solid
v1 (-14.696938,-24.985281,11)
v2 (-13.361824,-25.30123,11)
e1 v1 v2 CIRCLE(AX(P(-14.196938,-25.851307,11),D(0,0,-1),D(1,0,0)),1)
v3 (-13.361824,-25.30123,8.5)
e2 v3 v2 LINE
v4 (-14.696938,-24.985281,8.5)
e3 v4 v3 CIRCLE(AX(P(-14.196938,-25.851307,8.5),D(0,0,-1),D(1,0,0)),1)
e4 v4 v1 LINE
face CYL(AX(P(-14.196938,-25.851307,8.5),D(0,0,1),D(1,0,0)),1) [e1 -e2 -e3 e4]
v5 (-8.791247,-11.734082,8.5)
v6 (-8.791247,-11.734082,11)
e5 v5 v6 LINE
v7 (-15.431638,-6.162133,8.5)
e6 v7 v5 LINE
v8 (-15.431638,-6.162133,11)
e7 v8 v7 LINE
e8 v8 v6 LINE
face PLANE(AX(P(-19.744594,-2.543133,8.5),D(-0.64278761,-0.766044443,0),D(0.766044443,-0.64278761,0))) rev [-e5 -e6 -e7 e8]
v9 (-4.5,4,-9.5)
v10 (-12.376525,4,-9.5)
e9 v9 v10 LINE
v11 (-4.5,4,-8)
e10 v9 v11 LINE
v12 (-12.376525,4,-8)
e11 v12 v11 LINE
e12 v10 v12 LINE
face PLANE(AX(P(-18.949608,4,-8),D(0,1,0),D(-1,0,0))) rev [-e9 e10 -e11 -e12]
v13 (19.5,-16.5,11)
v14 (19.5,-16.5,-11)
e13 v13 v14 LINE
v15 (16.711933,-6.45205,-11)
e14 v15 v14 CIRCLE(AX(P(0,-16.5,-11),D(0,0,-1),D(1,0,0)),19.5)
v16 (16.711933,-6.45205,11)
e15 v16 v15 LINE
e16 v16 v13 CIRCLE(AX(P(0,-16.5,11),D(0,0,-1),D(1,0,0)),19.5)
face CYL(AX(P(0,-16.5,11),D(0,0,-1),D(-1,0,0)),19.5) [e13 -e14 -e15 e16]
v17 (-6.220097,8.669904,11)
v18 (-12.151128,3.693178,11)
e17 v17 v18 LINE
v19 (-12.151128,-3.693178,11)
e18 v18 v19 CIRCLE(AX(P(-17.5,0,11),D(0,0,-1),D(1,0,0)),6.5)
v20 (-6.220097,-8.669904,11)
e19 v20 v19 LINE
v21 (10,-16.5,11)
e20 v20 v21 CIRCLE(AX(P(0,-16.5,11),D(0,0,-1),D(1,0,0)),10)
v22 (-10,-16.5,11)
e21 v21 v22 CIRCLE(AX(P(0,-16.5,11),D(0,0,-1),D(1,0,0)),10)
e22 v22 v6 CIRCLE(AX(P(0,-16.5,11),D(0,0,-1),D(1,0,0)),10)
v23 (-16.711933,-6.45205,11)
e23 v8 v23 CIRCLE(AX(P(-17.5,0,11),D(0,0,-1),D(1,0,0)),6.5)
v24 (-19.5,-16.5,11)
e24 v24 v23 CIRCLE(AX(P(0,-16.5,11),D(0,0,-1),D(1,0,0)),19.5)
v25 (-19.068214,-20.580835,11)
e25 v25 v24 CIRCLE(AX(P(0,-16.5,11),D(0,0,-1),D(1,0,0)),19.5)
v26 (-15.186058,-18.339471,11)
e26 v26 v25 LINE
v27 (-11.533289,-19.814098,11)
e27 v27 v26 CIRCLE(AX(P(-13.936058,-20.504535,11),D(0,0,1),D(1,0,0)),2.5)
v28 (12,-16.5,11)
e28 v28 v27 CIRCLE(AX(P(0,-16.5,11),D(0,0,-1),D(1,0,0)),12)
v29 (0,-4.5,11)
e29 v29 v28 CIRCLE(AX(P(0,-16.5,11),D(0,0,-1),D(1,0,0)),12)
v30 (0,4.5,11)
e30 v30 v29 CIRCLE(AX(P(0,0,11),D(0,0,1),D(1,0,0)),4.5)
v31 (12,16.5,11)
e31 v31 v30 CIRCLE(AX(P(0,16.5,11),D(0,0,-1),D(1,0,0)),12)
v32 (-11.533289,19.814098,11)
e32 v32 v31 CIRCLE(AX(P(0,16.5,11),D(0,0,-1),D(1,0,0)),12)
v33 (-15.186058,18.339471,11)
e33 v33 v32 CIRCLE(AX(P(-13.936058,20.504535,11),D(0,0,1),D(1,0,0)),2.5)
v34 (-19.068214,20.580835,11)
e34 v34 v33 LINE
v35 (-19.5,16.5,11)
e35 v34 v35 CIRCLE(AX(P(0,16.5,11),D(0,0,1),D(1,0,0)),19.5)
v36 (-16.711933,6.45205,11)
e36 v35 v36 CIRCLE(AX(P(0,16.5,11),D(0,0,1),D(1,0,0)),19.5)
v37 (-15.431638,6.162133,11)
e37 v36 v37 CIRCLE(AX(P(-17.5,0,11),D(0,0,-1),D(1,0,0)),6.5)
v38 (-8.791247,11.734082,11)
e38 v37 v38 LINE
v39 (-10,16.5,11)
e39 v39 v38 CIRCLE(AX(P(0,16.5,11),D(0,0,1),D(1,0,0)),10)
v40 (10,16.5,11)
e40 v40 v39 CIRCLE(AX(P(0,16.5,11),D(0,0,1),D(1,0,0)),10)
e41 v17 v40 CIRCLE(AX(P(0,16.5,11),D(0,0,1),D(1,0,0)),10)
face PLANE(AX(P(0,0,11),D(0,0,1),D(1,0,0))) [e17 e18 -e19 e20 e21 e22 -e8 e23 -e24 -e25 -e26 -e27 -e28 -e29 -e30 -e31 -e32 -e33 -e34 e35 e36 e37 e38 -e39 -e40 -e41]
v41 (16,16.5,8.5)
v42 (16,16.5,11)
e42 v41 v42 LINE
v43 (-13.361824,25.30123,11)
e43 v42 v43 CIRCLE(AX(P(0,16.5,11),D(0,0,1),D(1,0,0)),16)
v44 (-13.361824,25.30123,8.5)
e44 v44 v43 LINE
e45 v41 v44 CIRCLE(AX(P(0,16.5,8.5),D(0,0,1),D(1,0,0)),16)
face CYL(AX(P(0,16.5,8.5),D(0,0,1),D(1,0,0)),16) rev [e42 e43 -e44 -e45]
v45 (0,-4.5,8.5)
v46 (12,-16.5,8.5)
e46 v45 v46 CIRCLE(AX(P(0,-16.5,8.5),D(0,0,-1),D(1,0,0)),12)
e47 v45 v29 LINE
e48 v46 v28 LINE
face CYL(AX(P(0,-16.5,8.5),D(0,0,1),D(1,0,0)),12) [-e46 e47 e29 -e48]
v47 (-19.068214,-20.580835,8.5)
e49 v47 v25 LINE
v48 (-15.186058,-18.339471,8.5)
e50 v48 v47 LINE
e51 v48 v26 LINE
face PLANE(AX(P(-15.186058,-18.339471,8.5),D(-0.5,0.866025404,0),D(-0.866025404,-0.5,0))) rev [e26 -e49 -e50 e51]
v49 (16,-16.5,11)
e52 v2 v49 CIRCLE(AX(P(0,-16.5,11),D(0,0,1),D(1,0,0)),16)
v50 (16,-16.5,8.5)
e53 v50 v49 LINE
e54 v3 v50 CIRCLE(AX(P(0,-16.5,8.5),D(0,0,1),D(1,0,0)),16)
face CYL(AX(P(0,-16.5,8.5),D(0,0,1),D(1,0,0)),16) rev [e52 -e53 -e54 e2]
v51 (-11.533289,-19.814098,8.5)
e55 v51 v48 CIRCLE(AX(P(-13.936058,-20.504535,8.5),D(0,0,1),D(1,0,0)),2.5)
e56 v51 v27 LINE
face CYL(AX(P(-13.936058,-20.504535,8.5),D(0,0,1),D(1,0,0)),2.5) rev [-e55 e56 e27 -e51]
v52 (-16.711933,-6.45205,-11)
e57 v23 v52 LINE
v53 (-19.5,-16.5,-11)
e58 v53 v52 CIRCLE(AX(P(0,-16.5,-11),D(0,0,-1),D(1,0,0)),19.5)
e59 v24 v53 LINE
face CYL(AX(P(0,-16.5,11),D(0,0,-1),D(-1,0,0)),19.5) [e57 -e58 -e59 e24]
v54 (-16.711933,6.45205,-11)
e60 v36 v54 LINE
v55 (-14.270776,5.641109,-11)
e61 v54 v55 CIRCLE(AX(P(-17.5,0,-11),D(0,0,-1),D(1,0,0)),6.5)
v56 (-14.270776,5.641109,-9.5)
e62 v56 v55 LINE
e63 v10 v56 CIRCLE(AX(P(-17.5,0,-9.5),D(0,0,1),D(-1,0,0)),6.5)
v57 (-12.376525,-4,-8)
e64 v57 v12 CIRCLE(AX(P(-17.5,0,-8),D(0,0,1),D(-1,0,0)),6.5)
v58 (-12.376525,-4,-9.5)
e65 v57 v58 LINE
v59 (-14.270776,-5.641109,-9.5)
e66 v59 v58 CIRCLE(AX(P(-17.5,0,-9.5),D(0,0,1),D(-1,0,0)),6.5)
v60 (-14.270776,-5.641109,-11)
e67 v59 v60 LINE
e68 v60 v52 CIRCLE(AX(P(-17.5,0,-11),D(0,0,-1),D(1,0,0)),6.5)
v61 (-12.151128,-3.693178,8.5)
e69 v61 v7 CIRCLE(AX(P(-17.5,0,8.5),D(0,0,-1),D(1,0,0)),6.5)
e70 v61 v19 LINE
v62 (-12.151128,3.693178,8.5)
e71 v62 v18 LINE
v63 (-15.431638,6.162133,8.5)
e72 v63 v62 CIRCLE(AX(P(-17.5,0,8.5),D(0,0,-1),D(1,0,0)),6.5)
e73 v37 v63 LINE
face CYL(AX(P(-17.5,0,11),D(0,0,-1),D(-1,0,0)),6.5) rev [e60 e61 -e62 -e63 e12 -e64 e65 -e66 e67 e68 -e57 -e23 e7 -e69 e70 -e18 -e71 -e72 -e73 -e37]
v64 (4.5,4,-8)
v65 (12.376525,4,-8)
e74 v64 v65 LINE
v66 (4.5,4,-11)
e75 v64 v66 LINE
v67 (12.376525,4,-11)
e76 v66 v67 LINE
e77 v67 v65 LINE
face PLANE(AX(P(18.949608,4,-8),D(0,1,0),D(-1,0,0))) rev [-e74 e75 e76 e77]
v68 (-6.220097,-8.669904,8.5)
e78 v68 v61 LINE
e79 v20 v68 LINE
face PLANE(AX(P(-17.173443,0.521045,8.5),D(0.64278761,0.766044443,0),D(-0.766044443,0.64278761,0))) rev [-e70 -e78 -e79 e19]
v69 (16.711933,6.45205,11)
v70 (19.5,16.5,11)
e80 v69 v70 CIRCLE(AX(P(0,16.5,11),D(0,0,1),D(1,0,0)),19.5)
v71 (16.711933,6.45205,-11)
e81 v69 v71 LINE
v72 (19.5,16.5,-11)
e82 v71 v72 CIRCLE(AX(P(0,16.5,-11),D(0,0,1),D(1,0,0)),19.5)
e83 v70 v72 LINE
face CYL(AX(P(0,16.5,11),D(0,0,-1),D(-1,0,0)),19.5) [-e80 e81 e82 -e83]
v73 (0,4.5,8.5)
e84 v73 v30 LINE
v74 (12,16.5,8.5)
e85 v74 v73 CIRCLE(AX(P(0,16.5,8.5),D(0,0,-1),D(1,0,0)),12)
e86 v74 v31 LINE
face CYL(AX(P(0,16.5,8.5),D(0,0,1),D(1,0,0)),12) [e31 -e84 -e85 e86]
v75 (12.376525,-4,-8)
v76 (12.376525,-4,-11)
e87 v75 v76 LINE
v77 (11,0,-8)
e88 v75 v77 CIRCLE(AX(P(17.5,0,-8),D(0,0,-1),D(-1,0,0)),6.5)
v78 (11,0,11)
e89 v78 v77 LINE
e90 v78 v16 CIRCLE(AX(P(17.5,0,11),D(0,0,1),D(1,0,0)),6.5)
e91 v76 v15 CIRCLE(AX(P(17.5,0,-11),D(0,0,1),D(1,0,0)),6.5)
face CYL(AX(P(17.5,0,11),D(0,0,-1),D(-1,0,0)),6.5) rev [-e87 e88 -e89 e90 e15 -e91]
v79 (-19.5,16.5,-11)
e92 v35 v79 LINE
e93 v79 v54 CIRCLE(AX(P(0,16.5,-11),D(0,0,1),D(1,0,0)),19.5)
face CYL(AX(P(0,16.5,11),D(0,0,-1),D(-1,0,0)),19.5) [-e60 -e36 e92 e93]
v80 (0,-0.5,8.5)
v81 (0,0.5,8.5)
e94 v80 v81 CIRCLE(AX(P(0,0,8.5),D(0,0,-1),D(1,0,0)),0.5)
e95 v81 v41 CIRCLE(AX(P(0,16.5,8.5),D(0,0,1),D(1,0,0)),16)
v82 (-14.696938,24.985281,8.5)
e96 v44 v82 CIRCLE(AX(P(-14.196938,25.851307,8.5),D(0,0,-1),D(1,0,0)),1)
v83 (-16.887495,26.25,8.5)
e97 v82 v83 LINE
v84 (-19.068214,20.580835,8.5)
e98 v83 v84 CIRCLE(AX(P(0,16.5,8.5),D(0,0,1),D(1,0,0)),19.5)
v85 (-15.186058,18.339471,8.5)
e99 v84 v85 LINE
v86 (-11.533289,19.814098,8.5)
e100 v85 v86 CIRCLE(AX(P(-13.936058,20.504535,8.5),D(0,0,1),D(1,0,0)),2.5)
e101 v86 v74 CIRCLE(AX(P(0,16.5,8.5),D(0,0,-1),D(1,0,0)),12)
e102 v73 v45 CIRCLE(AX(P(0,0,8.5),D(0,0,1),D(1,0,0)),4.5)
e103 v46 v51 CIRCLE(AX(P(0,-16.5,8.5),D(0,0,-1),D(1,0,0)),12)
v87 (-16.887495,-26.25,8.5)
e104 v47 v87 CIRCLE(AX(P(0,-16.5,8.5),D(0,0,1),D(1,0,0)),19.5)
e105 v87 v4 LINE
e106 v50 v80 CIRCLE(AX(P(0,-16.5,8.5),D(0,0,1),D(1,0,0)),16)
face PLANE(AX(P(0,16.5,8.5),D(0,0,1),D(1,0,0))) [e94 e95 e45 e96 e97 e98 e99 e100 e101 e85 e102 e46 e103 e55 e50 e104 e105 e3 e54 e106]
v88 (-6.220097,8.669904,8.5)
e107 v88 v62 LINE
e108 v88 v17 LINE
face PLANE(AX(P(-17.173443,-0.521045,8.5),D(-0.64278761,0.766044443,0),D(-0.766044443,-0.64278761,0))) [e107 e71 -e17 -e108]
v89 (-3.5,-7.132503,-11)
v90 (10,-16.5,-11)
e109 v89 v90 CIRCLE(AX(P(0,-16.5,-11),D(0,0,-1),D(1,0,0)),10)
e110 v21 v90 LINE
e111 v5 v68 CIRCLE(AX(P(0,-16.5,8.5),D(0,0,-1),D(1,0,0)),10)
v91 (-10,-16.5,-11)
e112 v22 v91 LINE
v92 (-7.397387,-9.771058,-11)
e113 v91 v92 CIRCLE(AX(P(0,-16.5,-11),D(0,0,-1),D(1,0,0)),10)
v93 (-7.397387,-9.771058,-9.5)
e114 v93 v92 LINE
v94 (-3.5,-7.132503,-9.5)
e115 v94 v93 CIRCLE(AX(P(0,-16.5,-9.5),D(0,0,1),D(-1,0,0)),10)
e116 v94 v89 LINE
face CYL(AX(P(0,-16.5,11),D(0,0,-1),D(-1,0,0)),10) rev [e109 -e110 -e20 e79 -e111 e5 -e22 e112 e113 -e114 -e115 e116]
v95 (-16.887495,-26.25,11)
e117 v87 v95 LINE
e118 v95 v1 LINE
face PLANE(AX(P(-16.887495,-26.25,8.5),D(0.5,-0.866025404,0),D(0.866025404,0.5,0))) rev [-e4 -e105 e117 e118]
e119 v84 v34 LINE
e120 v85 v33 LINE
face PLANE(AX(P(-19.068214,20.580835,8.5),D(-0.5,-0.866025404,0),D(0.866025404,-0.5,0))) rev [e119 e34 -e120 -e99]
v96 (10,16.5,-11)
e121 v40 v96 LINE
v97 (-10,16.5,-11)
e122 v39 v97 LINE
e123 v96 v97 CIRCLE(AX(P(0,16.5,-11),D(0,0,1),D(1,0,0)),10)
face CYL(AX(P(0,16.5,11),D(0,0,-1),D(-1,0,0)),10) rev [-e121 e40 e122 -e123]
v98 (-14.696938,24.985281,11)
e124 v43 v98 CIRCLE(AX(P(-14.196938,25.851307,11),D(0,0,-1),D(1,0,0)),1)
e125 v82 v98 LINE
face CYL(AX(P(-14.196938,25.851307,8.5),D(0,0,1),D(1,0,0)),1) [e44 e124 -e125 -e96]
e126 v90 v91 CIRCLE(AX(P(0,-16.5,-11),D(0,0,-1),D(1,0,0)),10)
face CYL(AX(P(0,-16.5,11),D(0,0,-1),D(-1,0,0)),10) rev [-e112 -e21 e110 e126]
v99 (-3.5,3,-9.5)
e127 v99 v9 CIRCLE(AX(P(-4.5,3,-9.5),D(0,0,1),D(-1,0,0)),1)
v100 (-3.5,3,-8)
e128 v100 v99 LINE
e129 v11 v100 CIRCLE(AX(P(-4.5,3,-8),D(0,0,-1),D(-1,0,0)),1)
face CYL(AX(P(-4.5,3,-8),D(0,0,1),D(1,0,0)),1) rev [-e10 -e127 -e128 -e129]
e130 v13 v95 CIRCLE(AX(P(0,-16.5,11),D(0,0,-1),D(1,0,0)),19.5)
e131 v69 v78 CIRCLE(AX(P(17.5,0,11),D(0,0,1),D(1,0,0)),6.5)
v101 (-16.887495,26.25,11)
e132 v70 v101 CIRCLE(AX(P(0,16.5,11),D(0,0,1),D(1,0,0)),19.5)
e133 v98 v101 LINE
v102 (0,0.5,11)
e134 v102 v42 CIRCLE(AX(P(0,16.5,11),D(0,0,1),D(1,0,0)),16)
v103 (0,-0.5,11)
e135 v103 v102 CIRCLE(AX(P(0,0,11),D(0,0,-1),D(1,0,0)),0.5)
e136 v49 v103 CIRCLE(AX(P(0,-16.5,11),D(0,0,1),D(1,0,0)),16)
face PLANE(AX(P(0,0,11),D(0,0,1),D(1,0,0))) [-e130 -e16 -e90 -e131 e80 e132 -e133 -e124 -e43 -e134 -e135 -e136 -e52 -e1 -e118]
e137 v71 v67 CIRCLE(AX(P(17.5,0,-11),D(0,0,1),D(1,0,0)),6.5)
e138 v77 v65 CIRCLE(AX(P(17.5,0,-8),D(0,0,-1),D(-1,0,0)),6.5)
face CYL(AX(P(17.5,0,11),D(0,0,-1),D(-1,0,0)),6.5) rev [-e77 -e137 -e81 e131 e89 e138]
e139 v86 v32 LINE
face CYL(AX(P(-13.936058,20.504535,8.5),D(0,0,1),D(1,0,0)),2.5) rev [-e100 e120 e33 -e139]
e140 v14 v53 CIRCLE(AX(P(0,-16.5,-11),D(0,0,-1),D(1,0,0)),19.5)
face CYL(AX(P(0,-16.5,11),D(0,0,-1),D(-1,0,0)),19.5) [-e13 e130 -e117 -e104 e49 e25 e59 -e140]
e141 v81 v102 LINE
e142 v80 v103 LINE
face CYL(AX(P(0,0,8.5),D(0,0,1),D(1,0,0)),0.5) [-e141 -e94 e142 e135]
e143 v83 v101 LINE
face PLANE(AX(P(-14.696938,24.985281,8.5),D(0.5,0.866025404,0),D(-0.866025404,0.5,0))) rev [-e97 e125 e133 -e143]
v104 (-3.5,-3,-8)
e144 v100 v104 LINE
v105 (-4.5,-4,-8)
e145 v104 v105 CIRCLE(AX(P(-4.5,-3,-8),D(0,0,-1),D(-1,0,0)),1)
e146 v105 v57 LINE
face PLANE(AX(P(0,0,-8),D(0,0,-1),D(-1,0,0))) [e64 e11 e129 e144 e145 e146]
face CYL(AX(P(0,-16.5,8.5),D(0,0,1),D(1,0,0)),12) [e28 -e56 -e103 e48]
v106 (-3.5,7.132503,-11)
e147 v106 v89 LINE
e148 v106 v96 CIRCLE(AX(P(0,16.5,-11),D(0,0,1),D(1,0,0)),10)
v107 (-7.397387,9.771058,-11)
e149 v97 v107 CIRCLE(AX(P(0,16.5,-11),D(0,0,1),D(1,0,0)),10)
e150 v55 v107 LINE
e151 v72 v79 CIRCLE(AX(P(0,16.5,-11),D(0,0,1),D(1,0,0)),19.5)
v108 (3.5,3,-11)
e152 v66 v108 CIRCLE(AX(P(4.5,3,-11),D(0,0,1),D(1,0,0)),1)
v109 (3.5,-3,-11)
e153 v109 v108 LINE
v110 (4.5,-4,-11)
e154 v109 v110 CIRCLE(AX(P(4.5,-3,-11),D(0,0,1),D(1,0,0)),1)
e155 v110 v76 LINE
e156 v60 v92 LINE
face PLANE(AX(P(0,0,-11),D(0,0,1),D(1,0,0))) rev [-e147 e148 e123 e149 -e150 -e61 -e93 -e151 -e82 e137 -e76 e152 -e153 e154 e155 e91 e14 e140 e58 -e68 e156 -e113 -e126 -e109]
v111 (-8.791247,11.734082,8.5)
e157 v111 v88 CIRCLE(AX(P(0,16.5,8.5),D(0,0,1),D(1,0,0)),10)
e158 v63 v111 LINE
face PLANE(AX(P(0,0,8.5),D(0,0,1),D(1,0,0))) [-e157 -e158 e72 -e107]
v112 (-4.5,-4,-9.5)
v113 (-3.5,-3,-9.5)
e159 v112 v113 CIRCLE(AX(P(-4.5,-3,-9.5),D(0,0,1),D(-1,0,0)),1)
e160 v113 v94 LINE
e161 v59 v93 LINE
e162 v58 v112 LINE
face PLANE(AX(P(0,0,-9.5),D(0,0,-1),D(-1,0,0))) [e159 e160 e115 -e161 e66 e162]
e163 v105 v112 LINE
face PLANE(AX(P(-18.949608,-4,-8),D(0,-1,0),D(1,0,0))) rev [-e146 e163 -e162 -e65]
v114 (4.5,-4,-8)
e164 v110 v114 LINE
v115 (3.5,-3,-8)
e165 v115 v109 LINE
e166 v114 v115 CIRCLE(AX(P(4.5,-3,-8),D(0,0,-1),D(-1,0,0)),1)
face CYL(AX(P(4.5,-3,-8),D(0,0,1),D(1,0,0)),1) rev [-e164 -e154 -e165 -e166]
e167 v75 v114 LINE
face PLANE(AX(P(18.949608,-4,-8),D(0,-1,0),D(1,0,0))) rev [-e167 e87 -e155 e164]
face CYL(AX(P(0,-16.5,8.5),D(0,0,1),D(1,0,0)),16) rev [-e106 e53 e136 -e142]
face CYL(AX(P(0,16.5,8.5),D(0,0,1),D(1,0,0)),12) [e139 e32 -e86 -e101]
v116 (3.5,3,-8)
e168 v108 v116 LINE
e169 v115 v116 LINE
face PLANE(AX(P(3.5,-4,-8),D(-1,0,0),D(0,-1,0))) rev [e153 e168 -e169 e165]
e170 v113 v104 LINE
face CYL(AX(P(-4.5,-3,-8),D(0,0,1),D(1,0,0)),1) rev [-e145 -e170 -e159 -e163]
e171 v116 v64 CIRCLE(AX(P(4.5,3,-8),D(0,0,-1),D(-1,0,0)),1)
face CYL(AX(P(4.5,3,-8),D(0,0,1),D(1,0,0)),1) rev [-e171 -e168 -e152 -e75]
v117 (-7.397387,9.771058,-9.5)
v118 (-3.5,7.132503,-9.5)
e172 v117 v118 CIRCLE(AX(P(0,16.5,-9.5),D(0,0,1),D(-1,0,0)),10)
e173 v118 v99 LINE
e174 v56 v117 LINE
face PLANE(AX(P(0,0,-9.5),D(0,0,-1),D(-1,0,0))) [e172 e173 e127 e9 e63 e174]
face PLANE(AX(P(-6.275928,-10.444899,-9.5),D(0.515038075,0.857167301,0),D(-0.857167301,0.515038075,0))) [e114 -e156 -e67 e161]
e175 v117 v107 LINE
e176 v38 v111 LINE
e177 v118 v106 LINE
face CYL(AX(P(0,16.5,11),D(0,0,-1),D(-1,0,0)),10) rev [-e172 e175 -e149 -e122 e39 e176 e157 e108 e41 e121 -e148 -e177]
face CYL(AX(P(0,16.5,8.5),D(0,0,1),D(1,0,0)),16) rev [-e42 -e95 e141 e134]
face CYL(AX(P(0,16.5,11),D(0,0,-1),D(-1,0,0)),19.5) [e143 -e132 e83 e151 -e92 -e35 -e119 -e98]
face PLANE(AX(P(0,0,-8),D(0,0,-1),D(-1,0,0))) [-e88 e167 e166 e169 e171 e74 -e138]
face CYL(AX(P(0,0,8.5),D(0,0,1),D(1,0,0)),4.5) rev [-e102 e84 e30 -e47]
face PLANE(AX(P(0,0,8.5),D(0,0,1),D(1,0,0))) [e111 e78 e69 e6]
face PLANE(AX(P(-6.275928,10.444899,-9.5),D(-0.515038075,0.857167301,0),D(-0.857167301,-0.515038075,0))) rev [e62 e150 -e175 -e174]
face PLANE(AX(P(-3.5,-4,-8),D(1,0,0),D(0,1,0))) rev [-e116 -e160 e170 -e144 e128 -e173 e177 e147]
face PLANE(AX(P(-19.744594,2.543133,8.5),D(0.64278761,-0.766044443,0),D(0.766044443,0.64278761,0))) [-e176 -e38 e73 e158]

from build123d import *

# Parameters (mm, degrees)
SKETCH1_R           = 10
BOSS_EXTRUDE1_DEPTH = 11
CUT_EXTRUDE1_DEPTH  = 2.5
CUT_EXTRUDE2_DEPTH  = 2.5
SKETCH4_W           = 15.449608091
SKETCH4_H           = 8
CUT_EXTRUDE3_DEPTH  = 3
FILLET1_R           = 1
CUT_EXTRUDE5_START  = -1.5
CUT_EXTRUDE5_DEPTH  = 1.5


with BuildPart() as part:
    # Sketch1 → Boss-Extrude1 (new, symmetric)
    with BuildSketch(Plane.XY):
        with BuildLine():
            ThreePointArc((16.711932938, -6.452050085), (11, 0), (16.711932938, 6.452050085))
            ThreePointArc((16.711932938, 6.452050085), (0, 36), (-16.711932938, 6.452050085))
            ThreePointArc((-16.711932938, 6.452050085), (-11, 0), (-16.711932938, -6.452050085))
            ThreePointArc((-16.711932938, -6.452050085), (0, -36), (16.711932938, -6.452050085))
        make_face()
        with Locations((0, -16.5)):
            Circle(SKETCH1_R, mode=Mode.SUBTRACT)
        with Locations((0, 16.5)):
            Circle(SKETCH1_R, mode=Mode.SUBTRACT)
    extrude(amount=BOSS_EXTRUDE1_DEPTH, both=True)

    # Sketch2 → Cut-Extrude1 (cut)
    with BuildSketch(Plane.XY.offset(11)):
        with BuildLine():
            Line((-19.068213964, 20.580835235), (-15.186057607, 18.339471217))
            ThreePointArc((-15.186057607, 18.339471217), (-13.000189211, 18.186313351), (-11.533289054, 19.814097705))
            ThreePointArc((-11.533289054, 19.814097705), (9.5856448, 23.719100621), (0, 4.5))
            ThreePointArc((0, 4.5), (-4.5, 0), (0, -4.5))
            ThreePointArc((0, -4.5), (9.5856448, -23.719100621), (-11.533289054, -19.814097705))
            ThreePointArc((-11.533289054, -19.814097705), (-13.000189211, -18.186313351), (-15.186057607, -18.339471217))
            Line((-15.186057607, -18.339471217), (-19.068213964, -20.580835235))
            ThreePointArc((-19.068213964, -20.580835235), (-18.199948236, -23.500848821), (-16.887495374, -26.25))
            Line((-16.887495374, -26.25), (-14.696938457, -24.985281374))
            ThreePointArc((-14.696938457, -24.985281374), (-13.966653368, -24.87818357), (-13.36182443, -25.301229909))
            ThreePointArc((-13.36182443, -25.301229909), (14.085802756, -24.088818138), (0, -0.5))
            ThreePointArc((0, -0.5), (-0.5, 0), (0, 0.5))
            ThreePointArc((0, 0.5), (14.085802756, 24.088818138), (-13.36182443, 25.301229909))
            ThreePointArc((-13.36182443, 25.301229909), (-13.966653368, 24.87818357), (-14.696938457, 24.985281374))
            Line((-14.696938457, 24.985281374), (-16.887495374, 26.25))
            ThreePointArc((-16.887495374, 26.25), (-18.199948236, 23.500848821), (-19.068213964, 20.580835235))
        make_face()
    extrude(amount=-CUT_EXTRUDE1_DEPTH, mode=Mode.SUBTRACT)

    # Sketch3 → Cut-Extrude2 (cut)
    with BuildSketch(Plane.XY.offset(11)):
        Polygon((-17.173443463, 0.521044654), (1.285575219, -14.967911114), (-1.285575219, -18.032088886), (-19.744593902, -2.543133118), align=None)
    cut_extrude2 = extrude(amount=-CUT_EXTRUDE2_DEPTH, mode=Mode.SUBTRACT)

    # Mirror1: Cut-Extrude2 across plane
    add(cut_extrude2.mirror(Plane.ZX), mode=Mode.SUBTRACT)

    # Sketch4 → Cut-Extrude3 (cut)
    with BuildSketch(Plane(origin=(0, 0, -11), x_dir=(-1, 0, 0), z_dir=(0, 0, -1))):
        with Locations((11.224804046, 0)):
            Rectangle(SKETCH4_W, SKETCH4_H)
        with Locations((-11.224804046, 0)):
            Rectangle(SKETCH4_W, SKETCH4_H)
    extrude(amount=-CUT_EXTRUDE3_DEPTH, mode=Mode.SUBTRACT)

    # Fillet1
    fillet1_edges = [part.edges().sort_by_distance(p)[0] for p in [
        (-3.5, 4, -9.5),
        (-3.5, -4, -9.5),
        (3.5, -4, -9.5),
        (3.5, 4, -9.5),
    ]]
    fillet(fillet1_edges, radius=FILLET1_R)

    # Sketch5 → Cut-Extrude5 (cut)
    with BuildSketch(Plane(origin=(0, 0, -11), x_dir=(-1, 0, 0), z_dir=(0, 0, -1)).offset(CUT_EXTRUDE5_START)):
        with BuildLine():
            ThreePointArc((12.376524617, 4), (13.243803843, 4.912717605), (14.270776222, 5.641109269))
            Line((14.270776222, 5.641109269), (7.397387325, 9.771057976))
            ThreePointArc((7.397387325, 9.771057976), (5.606135542, 8.219224415), (3.5, 7.132503002))
            Line((3.5, 7.132503002), (3.5, 3))
            ThreePointArc((3.5, 3), (3.792893219, 3.707106781), (4.5, 4))
            Line((4.5, 4), (12.376524617, 4))
        make_face()
        with BuildLine():
            Line((7.397387325, -9.771057976), (14.270776222, -5.641109269))
            ThreePointArc((14.270776222, -5.641109269), (13.243803843, -4.912717605), (12.376524617, -4))
            Line((12.376524617, -4), (4.5, -4))
            ThreePointArc((4.5, -4), (3.792893219, -3.707106781), (3.5, -3))
            Line((3.5, -3), (3.5, -7.132503002))
            ThreePointArc((3.5, -7.132503002), (5.606135542, -8.219224415), (7.397387325, -9.771057976))
        make_face()
    extrude(amount=CUT_EXTRUDE5_DEPTH, mode=Mode.SUBTRACT)


solid = part.part
